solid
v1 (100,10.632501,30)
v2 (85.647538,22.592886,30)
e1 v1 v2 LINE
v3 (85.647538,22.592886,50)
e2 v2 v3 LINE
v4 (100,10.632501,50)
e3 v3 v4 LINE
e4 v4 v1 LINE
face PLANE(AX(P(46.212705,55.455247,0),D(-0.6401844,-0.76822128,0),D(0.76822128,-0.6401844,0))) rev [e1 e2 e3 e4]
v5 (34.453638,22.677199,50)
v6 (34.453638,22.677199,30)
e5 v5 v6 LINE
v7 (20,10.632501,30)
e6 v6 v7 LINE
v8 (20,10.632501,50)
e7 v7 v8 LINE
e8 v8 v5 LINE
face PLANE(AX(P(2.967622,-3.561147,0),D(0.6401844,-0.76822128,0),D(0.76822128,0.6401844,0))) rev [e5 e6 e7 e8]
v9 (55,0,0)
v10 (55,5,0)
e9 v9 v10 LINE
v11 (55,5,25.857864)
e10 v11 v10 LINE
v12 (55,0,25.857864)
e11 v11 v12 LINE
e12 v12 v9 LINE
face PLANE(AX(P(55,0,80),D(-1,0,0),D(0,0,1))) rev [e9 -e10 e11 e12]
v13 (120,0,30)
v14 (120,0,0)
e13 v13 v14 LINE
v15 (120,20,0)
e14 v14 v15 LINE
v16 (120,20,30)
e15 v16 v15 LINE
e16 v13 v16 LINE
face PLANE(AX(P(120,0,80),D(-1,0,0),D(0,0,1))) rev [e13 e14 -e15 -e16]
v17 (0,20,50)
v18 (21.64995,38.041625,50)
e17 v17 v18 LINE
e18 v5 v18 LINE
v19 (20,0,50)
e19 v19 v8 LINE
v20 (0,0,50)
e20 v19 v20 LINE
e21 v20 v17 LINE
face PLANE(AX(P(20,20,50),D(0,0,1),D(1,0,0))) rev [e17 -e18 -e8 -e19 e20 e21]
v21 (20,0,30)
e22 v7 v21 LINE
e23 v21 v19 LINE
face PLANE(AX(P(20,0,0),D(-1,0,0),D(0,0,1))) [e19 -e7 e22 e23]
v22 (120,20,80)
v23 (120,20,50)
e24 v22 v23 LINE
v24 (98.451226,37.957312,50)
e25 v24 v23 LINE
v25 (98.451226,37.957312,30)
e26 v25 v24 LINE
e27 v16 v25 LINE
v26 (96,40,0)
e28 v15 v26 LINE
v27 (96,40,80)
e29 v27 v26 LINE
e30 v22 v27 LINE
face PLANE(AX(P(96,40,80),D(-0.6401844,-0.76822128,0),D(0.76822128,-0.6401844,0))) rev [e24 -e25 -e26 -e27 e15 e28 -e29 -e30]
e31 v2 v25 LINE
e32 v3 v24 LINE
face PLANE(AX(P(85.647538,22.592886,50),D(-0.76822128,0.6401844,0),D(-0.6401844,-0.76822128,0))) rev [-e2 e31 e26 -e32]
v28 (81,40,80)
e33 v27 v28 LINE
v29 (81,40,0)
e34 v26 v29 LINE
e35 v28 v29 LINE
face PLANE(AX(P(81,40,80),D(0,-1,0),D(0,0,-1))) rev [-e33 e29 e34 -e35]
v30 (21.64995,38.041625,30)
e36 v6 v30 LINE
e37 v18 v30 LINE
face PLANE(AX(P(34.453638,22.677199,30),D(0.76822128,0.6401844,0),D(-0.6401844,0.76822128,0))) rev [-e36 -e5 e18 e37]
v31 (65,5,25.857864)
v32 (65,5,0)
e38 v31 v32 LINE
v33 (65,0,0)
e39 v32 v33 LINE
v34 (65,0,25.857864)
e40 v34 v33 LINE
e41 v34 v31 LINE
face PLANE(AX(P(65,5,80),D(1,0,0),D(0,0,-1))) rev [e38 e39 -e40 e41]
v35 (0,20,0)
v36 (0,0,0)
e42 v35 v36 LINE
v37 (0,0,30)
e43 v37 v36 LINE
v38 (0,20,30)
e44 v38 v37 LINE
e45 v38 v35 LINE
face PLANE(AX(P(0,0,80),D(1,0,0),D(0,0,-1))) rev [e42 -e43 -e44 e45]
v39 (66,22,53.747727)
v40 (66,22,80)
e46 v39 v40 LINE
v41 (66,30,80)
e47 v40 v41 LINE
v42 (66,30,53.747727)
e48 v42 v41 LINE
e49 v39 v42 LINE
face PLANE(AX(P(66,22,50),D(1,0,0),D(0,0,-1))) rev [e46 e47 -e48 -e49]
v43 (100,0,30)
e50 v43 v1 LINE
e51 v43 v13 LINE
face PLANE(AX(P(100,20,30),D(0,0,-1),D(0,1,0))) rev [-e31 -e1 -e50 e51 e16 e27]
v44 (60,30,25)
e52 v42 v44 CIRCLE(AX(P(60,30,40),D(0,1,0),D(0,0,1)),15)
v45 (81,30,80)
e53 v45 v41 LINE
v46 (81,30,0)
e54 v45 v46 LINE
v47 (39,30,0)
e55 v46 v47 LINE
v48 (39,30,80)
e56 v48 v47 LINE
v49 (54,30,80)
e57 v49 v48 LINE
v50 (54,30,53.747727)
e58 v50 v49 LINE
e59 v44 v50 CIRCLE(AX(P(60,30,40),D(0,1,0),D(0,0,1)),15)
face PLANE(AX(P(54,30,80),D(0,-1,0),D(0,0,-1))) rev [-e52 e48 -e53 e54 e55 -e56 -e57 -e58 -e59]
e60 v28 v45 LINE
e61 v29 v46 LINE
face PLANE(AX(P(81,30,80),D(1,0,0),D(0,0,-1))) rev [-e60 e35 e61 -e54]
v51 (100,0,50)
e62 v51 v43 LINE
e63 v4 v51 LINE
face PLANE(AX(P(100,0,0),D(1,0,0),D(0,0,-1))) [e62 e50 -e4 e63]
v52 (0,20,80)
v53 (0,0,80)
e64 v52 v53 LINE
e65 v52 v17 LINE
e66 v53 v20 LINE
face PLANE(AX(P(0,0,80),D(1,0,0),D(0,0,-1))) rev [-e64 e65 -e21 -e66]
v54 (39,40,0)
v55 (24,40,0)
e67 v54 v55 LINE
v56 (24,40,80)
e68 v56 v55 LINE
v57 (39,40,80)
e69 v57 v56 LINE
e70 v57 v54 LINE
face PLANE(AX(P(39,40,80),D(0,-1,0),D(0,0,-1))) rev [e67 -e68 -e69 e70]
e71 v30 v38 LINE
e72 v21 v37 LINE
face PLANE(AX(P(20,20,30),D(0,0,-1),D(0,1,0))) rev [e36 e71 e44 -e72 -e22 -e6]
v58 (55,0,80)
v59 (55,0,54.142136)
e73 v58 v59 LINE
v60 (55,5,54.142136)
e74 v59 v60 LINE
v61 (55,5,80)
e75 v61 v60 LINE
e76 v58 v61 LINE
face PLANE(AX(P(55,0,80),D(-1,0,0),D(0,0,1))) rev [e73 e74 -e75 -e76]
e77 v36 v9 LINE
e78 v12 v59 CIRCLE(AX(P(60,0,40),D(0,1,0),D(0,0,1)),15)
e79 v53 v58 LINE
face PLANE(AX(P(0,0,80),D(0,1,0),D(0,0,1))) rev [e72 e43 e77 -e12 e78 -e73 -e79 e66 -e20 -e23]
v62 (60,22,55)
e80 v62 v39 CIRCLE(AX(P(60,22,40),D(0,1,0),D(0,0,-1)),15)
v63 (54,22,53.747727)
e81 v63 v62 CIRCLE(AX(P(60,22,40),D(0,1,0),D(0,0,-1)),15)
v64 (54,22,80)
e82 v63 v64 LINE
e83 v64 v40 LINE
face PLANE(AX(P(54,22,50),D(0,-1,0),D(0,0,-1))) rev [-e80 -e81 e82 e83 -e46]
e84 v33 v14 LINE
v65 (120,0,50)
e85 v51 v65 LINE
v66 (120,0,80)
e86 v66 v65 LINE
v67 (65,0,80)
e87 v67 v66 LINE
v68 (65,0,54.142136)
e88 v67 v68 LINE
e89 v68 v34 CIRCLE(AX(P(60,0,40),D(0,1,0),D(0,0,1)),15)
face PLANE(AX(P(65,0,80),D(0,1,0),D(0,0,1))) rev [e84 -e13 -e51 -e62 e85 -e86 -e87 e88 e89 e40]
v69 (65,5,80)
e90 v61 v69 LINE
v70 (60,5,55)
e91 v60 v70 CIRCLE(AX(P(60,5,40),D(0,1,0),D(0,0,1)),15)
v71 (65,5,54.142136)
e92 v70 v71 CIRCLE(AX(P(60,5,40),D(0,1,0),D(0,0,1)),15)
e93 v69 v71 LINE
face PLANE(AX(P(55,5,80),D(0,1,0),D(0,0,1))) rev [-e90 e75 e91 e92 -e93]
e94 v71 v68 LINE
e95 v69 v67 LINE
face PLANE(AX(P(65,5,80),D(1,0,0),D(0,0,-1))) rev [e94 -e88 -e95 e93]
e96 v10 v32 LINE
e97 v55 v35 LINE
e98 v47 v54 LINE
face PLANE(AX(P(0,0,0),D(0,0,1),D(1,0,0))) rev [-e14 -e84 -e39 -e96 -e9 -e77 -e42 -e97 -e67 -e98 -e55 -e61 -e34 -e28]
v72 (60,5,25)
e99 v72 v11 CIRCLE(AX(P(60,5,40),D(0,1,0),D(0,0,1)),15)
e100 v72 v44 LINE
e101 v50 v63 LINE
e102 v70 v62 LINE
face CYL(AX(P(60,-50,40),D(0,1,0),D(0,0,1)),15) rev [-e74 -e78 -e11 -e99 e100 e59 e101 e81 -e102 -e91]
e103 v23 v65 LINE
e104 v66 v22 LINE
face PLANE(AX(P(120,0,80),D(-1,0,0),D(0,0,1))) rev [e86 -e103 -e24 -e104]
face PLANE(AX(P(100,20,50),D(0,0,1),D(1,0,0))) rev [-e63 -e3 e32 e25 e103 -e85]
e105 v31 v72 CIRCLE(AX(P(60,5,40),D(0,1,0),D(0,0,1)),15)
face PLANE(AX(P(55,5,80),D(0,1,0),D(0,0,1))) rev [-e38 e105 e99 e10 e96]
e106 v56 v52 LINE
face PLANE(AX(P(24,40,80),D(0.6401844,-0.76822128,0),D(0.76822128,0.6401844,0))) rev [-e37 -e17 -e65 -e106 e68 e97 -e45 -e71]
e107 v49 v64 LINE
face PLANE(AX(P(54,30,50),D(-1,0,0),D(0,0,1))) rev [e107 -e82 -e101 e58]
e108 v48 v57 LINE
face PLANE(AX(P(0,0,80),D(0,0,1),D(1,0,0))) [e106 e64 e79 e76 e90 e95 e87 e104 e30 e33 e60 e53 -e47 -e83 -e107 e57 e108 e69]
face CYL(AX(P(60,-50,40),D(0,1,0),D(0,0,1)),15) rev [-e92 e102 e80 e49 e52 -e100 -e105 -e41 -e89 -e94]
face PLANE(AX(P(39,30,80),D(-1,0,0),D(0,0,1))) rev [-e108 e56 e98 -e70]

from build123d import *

# Parameters (mm, degrees)
BLOCK_BODY_EXTRUDE_80_DEPTH     = 80
THROUGH_CUT_SKETCH_R            = 15
THROUGH_CUT_80_DEPTH            = 80
PROFILE_CUT_30_DEPTH            = 30
POCKET_A_SKETCH_30X30_W         = 20
POCKET_A_SKETCH_30X30_H         = 20
SQUARE_POCKET_A_30X30X20_DEPTH  = 20
POCKET_A_EXTENSION_SKETCH_W     = 28.050217784
POCKET_A_EXTENSION_SKETCH_H     = 20
POCKET_A_EXTENSION_CUT_20_DEPTH = 20
POCKET_B_SKETCH_30X30_W         = 20
POCKET_B_SKETCH_30X30_H         = 20
SQUARE_POCKET_B_30X30X20_DEPTH  = 20
POCKET_B_EXTENSION_SKETCH_W     = 28.181918945
POCKET_B_EXTENSION_SKETCH_H     = 20
POCKET_B_EXTENSION_CUT_20_DEPTH = 20


with BuildPart() as part:
    # Block Profile Sketch → Block Body Extrude 80 (new body)
    with BuildSketch(Plane.XY):
        Polygon((0, 0), (0, 20), (24, 40), (39, 40), (39, 30), (54, 30), (66, 30), (81, 30), (81, 40), (96, 40), (120, 20), (120, 0), (65, 0), (65, 5), (55, 5), (55, 0), align=None)
    extrude(amount=BLOCK_BODY_EXTRUDE_80_DEPTH)

    # Through Cut Sketch → Through Cut 80 (cut)
    with BuildSketch(Plane(origin=(0, 30, 0), x_dir=(1, 0, 0), z_dir=(0, 1, 0))):
        with Locations(Location((60, -40, 0), (0, 0, 270))):
            Circle(THROUGH_CUT_SKETCH_R)
    extrude(amount=-THROUGH_CUT_80_DEPTH, mode=Mode.SUBTRACT)

    # Profile Cut Sketch → Profile Cut 30 (cut)
    with BuildSketch(Plane.XY.offset(80)):
        Polygon((60, 30), (66, 30), (66, 22), (54, 22), (54, 30), align=None)
    extrude(amount=-PROFILE_CUT_30_DEPTH, mode=Mode.SUBTRACT)

    # Pocket A Sketch 30x30 → Square Pocket A 30x30x20 (cut)
    with BuildSketch(Plane(origin=(120, 0, 0), x_dir=(0, 0, -1), z_dir=(1, 0, 0))):
        with Locations((-40, 10)):
            Rectangle(POCKET_A_SKETCH_30X30_W, POCKET_A_SKETCH_30X30_H)
    extrude(amount=-SQUARE_POCKET_A_30X30X20_DEPTH, mode=Mode.SUBTRACT)

    # Pocket A Extension Sketch → Pocket A Extension Cut 20 (cut)
    with BuildSketch(Plane(origin=(59.016393443, 70.819672131, 0), x_dir=(0.7682212795973757, -0.6401843996644799, 0), z_dir=(0.6401843996644799, 0.7682212795973757, 0))):
        with Locations((65.357756666, -40)):
            Rectangle(POCKET_A_EXTENSION_SKETCH_W, POCKET_A_EXTENSION_SKETCH_H)
    extrude(amount=-POCKET_A_EXTENSION_CUT_20_DEPTH, mode=Mode.SUBTRACT)

    # Pocket B Sketch 30x30 → Square Pocket B 30x30x20 (cut)
    with BuildSketch(Plane.ZY):
        with Locations((40, 10)):
            Rectangle(POCKET_B_SKETCH_30X30_W, POCKET_B_SKETCH_30X30_H)
    extrude(amount=-SQUARE_POCKET_B_30X30X20_DEPTH, mode=Mode.SUBTRACT)

    # Pocket B Extension Sketch → Pocket B Extension Cut 20 (cut)
    with BuildSketch(Plane(origin=(-9.836065574, 11.803278689, 0), x_dir=(0.7682212795973757, 0.6401843996644802, 0), z_dir=(-0.64018439966448, 0.7682212795973756, 0))):
        with Locations((26.894647466, -40)):
            Rectangle(POCKET_B_EXTENSION_SKETCH_W, POCKET_B_EXTENSION_SKETCH_H)
    extrude(amount=-POCKET_B_EXTENSION_CUT_20_DEPTH, mode=Mode.SUBTRACT)


solid = part.part
